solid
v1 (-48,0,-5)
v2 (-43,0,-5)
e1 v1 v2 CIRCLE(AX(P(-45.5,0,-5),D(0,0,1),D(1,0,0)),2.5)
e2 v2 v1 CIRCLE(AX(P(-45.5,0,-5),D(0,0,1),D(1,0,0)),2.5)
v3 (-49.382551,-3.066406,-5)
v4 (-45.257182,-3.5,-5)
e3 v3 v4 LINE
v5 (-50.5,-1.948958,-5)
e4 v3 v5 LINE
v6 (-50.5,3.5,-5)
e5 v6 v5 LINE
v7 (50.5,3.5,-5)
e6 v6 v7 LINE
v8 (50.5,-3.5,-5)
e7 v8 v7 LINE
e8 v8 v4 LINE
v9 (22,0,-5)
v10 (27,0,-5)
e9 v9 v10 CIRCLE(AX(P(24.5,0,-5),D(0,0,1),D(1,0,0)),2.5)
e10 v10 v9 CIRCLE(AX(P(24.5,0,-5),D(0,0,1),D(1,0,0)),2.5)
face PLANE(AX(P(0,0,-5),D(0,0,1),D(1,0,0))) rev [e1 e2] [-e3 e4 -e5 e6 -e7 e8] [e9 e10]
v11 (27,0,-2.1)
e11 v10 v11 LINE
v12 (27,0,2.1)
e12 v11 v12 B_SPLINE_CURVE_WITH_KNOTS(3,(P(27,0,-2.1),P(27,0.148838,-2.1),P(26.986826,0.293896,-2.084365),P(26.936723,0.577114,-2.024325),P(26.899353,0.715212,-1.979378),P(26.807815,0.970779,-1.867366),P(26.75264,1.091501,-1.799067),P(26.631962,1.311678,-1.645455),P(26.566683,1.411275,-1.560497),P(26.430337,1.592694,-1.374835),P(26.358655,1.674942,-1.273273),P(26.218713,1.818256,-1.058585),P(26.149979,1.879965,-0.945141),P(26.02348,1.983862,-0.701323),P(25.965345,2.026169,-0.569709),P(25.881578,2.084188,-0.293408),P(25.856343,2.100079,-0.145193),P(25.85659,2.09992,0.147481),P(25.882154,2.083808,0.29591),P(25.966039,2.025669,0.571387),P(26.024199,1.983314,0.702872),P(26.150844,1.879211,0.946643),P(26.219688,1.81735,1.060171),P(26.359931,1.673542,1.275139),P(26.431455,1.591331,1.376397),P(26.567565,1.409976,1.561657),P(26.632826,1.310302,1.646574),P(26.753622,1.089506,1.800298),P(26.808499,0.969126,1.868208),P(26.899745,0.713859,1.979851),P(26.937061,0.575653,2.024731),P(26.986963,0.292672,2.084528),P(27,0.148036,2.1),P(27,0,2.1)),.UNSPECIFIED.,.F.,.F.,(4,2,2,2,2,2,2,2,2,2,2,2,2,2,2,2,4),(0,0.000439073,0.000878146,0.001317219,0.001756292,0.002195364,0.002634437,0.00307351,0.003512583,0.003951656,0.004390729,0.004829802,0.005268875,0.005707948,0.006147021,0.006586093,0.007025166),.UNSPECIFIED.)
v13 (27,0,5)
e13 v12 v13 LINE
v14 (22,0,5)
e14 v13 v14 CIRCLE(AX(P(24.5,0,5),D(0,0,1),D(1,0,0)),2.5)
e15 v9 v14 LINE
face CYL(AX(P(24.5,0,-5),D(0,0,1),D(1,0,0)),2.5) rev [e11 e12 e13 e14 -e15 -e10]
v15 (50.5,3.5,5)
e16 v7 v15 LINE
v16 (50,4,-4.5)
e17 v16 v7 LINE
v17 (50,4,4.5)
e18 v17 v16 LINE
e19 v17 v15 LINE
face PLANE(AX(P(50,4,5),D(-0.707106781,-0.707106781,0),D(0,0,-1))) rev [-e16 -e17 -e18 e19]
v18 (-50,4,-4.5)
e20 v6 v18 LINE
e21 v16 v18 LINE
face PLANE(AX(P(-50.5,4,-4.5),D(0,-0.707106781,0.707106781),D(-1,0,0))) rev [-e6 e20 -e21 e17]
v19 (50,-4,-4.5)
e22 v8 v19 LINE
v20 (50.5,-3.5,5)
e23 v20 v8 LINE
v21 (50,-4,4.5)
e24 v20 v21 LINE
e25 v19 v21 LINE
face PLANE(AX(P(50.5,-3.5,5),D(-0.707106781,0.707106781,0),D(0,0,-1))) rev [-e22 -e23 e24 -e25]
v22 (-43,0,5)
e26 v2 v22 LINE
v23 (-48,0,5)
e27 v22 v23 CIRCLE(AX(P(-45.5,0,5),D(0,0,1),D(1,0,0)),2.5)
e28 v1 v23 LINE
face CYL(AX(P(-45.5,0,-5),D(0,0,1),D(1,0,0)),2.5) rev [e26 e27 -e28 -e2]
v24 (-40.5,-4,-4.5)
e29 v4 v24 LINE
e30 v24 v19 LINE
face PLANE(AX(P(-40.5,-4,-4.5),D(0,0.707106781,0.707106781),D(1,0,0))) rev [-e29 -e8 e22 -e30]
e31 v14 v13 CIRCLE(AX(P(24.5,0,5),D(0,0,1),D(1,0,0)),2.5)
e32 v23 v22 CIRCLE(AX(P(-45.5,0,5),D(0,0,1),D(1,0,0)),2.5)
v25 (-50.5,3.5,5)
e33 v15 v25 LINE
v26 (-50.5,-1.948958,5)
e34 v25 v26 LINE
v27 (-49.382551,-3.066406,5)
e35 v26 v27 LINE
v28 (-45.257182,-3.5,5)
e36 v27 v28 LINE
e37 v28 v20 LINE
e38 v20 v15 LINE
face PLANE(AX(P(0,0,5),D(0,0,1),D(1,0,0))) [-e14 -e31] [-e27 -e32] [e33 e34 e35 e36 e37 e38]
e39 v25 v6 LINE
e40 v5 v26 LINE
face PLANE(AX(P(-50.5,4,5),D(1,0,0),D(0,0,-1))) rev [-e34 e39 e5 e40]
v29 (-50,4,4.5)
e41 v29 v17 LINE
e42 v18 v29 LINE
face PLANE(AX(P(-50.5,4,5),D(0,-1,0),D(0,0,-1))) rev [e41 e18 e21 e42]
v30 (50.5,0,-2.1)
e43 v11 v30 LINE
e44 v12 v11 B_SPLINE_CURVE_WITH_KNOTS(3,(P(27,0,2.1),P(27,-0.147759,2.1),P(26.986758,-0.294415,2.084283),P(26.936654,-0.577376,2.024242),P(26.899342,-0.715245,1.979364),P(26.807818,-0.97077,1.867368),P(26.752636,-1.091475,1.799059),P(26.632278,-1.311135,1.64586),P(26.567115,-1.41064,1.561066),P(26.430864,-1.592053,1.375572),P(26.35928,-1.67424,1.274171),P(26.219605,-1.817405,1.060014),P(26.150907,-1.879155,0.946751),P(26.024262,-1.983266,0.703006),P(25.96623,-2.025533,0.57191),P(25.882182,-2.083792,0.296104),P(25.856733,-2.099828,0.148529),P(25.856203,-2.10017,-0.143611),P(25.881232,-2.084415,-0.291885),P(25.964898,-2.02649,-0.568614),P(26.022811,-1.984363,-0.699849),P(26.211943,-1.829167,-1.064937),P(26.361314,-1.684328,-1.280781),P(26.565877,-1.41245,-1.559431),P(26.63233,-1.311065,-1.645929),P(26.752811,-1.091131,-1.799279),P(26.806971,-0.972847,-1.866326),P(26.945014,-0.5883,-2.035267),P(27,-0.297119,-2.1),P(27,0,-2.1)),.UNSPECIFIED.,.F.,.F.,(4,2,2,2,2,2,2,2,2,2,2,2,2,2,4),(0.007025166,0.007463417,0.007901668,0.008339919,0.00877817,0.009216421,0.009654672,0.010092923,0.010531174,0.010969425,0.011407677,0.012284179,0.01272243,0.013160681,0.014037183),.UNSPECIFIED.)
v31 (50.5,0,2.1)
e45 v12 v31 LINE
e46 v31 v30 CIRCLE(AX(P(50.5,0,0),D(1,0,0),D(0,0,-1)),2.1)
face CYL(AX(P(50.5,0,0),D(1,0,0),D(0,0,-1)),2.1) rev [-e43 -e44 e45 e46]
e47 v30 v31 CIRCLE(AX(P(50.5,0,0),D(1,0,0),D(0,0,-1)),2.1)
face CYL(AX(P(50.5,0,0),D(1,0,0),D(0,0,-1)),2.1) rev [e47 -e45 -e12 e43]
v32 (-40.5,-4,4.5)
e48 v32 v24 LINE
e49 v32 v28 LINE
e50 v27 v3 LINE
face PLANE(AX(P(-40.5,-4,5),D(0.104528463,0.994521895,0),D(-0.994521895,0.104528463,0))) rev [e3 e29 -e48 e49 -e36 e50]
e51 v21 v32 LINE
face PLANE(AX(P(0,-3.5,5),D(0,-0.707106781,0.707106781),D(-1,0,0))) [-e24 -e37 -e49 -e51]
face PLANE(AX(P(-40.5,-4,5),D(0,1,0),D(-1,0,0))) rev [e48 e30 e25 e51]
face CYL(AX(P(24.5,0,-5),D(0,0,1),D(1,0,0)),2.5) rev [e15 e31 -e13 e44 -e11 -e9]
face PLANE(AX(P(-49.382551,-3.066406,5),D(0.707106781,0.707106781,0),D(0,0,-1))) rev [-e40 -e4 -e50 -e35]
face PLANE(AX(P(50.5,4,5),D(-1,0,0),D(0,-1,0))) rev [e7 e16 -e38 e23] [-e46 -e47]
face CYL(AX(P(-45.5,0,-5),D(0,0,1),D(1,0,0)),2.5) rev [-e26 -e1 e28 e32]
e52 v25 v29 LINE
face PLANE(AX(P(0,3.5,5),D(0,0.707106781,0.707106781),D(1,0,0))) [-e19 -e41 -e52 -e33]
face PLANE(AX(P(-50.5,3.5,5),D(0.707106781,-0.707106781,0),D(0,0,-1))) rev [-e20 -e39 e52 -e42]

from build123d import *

# Parameters (mm, degrees)
BOSS_EXTRUDE1_DEPTH   = 5
SKETCH2_R             = 2.5
CUT_EXTRUDE1_DEPTH    = 52.635743434
CHAMFER1_SIZE         = 0.5
CHAMFER2_SIZE         = 1
CHAMFER2_SIZE2        = 1.123603797
M5_TAPPED_HOLE1_D     = 4.2
M5_TAPPED_HOLE1_DEPTH = 26
M5_TAPPED_HOLE1_TIP   = 1.2618073


with BuildPart() as part:
    # Sketch1 → Boss-Extrude1 (new, symmetric)
    with BuildSketch(Plane.XY):
        Polygon((-40.5, -4), (-50.5, -2.948957647), (-50.5, 4), (50.5, 4), (50.5, -4), align=None)
    extrude(amount=BOSS_EXTRUDE1_DEPTH, both=True)

    # Sketch2 → Cut-Extrude1 (cut, through all)
    with BuildSketch(Plane.XY.offset(5)):
        with Locations((-45.5, 0)):
            Circle(SKETCH2_R)
        with Locations((24.5, 0)):
            Circle(SKETCH2_R)
    extrude(amount=-CUT_EXTRUDE1_DEPTH, mode=Mode.SUBTRACT)

    # Chamfer1
    chamfer1_edges = [part.edges().sort_by_distance(p)[0] for p in [
        (5, -4, 5),
        (5, -4, -5),
        (0, 4, -5),
        (0, 4, 5),
        (50.5, -4, 0),
        (-50.5, 4, 0),
        (50.5, 4, 0),
    ]]
    chamfer(chamfer1_edges, length=CHAMFER1_SIZE)

    # Chamfer2
    chamfer2_edges = [part.edges().sort_by_distance(p)[0] for p in [
        (-50.5, -2.948957647, 0),
    ]]
    chamfer2_side = [part.faces().sort_by_distance(p)[0] for p in [
        (-50.5, 0.275521176, 0),
    ]]
    chamfer(chamfer2_edges, length=CHAMFER2_SIZE, length2=CHAMFER2_SIZE2, reference=chamfer2_side[0])

    # M5 Tapped Hole1
    with Locations(Plane(origin=(50.5, 0, 0), x_dir=(0, 0, -1), z_dir=(1, 0, 0))):
        with Locations((0, 0)):
            Hole(M5_TAPPED_HOLE1_D / 2, depth=M5_TAPPED_HOLE1_DEPTH)
            with Locations((0, 0, -(M5_TAPPED_HOLE1_DEPTH + M5_TAPPED_HOLE1_TIP / 2))):  # 118° drill point
                Cone(0, M5_TAPPED_HOLE1_D / 2, M5_TAPPED_HOLE1_TIP, mode=Mode.SUBTRACT)


solid = part.part
